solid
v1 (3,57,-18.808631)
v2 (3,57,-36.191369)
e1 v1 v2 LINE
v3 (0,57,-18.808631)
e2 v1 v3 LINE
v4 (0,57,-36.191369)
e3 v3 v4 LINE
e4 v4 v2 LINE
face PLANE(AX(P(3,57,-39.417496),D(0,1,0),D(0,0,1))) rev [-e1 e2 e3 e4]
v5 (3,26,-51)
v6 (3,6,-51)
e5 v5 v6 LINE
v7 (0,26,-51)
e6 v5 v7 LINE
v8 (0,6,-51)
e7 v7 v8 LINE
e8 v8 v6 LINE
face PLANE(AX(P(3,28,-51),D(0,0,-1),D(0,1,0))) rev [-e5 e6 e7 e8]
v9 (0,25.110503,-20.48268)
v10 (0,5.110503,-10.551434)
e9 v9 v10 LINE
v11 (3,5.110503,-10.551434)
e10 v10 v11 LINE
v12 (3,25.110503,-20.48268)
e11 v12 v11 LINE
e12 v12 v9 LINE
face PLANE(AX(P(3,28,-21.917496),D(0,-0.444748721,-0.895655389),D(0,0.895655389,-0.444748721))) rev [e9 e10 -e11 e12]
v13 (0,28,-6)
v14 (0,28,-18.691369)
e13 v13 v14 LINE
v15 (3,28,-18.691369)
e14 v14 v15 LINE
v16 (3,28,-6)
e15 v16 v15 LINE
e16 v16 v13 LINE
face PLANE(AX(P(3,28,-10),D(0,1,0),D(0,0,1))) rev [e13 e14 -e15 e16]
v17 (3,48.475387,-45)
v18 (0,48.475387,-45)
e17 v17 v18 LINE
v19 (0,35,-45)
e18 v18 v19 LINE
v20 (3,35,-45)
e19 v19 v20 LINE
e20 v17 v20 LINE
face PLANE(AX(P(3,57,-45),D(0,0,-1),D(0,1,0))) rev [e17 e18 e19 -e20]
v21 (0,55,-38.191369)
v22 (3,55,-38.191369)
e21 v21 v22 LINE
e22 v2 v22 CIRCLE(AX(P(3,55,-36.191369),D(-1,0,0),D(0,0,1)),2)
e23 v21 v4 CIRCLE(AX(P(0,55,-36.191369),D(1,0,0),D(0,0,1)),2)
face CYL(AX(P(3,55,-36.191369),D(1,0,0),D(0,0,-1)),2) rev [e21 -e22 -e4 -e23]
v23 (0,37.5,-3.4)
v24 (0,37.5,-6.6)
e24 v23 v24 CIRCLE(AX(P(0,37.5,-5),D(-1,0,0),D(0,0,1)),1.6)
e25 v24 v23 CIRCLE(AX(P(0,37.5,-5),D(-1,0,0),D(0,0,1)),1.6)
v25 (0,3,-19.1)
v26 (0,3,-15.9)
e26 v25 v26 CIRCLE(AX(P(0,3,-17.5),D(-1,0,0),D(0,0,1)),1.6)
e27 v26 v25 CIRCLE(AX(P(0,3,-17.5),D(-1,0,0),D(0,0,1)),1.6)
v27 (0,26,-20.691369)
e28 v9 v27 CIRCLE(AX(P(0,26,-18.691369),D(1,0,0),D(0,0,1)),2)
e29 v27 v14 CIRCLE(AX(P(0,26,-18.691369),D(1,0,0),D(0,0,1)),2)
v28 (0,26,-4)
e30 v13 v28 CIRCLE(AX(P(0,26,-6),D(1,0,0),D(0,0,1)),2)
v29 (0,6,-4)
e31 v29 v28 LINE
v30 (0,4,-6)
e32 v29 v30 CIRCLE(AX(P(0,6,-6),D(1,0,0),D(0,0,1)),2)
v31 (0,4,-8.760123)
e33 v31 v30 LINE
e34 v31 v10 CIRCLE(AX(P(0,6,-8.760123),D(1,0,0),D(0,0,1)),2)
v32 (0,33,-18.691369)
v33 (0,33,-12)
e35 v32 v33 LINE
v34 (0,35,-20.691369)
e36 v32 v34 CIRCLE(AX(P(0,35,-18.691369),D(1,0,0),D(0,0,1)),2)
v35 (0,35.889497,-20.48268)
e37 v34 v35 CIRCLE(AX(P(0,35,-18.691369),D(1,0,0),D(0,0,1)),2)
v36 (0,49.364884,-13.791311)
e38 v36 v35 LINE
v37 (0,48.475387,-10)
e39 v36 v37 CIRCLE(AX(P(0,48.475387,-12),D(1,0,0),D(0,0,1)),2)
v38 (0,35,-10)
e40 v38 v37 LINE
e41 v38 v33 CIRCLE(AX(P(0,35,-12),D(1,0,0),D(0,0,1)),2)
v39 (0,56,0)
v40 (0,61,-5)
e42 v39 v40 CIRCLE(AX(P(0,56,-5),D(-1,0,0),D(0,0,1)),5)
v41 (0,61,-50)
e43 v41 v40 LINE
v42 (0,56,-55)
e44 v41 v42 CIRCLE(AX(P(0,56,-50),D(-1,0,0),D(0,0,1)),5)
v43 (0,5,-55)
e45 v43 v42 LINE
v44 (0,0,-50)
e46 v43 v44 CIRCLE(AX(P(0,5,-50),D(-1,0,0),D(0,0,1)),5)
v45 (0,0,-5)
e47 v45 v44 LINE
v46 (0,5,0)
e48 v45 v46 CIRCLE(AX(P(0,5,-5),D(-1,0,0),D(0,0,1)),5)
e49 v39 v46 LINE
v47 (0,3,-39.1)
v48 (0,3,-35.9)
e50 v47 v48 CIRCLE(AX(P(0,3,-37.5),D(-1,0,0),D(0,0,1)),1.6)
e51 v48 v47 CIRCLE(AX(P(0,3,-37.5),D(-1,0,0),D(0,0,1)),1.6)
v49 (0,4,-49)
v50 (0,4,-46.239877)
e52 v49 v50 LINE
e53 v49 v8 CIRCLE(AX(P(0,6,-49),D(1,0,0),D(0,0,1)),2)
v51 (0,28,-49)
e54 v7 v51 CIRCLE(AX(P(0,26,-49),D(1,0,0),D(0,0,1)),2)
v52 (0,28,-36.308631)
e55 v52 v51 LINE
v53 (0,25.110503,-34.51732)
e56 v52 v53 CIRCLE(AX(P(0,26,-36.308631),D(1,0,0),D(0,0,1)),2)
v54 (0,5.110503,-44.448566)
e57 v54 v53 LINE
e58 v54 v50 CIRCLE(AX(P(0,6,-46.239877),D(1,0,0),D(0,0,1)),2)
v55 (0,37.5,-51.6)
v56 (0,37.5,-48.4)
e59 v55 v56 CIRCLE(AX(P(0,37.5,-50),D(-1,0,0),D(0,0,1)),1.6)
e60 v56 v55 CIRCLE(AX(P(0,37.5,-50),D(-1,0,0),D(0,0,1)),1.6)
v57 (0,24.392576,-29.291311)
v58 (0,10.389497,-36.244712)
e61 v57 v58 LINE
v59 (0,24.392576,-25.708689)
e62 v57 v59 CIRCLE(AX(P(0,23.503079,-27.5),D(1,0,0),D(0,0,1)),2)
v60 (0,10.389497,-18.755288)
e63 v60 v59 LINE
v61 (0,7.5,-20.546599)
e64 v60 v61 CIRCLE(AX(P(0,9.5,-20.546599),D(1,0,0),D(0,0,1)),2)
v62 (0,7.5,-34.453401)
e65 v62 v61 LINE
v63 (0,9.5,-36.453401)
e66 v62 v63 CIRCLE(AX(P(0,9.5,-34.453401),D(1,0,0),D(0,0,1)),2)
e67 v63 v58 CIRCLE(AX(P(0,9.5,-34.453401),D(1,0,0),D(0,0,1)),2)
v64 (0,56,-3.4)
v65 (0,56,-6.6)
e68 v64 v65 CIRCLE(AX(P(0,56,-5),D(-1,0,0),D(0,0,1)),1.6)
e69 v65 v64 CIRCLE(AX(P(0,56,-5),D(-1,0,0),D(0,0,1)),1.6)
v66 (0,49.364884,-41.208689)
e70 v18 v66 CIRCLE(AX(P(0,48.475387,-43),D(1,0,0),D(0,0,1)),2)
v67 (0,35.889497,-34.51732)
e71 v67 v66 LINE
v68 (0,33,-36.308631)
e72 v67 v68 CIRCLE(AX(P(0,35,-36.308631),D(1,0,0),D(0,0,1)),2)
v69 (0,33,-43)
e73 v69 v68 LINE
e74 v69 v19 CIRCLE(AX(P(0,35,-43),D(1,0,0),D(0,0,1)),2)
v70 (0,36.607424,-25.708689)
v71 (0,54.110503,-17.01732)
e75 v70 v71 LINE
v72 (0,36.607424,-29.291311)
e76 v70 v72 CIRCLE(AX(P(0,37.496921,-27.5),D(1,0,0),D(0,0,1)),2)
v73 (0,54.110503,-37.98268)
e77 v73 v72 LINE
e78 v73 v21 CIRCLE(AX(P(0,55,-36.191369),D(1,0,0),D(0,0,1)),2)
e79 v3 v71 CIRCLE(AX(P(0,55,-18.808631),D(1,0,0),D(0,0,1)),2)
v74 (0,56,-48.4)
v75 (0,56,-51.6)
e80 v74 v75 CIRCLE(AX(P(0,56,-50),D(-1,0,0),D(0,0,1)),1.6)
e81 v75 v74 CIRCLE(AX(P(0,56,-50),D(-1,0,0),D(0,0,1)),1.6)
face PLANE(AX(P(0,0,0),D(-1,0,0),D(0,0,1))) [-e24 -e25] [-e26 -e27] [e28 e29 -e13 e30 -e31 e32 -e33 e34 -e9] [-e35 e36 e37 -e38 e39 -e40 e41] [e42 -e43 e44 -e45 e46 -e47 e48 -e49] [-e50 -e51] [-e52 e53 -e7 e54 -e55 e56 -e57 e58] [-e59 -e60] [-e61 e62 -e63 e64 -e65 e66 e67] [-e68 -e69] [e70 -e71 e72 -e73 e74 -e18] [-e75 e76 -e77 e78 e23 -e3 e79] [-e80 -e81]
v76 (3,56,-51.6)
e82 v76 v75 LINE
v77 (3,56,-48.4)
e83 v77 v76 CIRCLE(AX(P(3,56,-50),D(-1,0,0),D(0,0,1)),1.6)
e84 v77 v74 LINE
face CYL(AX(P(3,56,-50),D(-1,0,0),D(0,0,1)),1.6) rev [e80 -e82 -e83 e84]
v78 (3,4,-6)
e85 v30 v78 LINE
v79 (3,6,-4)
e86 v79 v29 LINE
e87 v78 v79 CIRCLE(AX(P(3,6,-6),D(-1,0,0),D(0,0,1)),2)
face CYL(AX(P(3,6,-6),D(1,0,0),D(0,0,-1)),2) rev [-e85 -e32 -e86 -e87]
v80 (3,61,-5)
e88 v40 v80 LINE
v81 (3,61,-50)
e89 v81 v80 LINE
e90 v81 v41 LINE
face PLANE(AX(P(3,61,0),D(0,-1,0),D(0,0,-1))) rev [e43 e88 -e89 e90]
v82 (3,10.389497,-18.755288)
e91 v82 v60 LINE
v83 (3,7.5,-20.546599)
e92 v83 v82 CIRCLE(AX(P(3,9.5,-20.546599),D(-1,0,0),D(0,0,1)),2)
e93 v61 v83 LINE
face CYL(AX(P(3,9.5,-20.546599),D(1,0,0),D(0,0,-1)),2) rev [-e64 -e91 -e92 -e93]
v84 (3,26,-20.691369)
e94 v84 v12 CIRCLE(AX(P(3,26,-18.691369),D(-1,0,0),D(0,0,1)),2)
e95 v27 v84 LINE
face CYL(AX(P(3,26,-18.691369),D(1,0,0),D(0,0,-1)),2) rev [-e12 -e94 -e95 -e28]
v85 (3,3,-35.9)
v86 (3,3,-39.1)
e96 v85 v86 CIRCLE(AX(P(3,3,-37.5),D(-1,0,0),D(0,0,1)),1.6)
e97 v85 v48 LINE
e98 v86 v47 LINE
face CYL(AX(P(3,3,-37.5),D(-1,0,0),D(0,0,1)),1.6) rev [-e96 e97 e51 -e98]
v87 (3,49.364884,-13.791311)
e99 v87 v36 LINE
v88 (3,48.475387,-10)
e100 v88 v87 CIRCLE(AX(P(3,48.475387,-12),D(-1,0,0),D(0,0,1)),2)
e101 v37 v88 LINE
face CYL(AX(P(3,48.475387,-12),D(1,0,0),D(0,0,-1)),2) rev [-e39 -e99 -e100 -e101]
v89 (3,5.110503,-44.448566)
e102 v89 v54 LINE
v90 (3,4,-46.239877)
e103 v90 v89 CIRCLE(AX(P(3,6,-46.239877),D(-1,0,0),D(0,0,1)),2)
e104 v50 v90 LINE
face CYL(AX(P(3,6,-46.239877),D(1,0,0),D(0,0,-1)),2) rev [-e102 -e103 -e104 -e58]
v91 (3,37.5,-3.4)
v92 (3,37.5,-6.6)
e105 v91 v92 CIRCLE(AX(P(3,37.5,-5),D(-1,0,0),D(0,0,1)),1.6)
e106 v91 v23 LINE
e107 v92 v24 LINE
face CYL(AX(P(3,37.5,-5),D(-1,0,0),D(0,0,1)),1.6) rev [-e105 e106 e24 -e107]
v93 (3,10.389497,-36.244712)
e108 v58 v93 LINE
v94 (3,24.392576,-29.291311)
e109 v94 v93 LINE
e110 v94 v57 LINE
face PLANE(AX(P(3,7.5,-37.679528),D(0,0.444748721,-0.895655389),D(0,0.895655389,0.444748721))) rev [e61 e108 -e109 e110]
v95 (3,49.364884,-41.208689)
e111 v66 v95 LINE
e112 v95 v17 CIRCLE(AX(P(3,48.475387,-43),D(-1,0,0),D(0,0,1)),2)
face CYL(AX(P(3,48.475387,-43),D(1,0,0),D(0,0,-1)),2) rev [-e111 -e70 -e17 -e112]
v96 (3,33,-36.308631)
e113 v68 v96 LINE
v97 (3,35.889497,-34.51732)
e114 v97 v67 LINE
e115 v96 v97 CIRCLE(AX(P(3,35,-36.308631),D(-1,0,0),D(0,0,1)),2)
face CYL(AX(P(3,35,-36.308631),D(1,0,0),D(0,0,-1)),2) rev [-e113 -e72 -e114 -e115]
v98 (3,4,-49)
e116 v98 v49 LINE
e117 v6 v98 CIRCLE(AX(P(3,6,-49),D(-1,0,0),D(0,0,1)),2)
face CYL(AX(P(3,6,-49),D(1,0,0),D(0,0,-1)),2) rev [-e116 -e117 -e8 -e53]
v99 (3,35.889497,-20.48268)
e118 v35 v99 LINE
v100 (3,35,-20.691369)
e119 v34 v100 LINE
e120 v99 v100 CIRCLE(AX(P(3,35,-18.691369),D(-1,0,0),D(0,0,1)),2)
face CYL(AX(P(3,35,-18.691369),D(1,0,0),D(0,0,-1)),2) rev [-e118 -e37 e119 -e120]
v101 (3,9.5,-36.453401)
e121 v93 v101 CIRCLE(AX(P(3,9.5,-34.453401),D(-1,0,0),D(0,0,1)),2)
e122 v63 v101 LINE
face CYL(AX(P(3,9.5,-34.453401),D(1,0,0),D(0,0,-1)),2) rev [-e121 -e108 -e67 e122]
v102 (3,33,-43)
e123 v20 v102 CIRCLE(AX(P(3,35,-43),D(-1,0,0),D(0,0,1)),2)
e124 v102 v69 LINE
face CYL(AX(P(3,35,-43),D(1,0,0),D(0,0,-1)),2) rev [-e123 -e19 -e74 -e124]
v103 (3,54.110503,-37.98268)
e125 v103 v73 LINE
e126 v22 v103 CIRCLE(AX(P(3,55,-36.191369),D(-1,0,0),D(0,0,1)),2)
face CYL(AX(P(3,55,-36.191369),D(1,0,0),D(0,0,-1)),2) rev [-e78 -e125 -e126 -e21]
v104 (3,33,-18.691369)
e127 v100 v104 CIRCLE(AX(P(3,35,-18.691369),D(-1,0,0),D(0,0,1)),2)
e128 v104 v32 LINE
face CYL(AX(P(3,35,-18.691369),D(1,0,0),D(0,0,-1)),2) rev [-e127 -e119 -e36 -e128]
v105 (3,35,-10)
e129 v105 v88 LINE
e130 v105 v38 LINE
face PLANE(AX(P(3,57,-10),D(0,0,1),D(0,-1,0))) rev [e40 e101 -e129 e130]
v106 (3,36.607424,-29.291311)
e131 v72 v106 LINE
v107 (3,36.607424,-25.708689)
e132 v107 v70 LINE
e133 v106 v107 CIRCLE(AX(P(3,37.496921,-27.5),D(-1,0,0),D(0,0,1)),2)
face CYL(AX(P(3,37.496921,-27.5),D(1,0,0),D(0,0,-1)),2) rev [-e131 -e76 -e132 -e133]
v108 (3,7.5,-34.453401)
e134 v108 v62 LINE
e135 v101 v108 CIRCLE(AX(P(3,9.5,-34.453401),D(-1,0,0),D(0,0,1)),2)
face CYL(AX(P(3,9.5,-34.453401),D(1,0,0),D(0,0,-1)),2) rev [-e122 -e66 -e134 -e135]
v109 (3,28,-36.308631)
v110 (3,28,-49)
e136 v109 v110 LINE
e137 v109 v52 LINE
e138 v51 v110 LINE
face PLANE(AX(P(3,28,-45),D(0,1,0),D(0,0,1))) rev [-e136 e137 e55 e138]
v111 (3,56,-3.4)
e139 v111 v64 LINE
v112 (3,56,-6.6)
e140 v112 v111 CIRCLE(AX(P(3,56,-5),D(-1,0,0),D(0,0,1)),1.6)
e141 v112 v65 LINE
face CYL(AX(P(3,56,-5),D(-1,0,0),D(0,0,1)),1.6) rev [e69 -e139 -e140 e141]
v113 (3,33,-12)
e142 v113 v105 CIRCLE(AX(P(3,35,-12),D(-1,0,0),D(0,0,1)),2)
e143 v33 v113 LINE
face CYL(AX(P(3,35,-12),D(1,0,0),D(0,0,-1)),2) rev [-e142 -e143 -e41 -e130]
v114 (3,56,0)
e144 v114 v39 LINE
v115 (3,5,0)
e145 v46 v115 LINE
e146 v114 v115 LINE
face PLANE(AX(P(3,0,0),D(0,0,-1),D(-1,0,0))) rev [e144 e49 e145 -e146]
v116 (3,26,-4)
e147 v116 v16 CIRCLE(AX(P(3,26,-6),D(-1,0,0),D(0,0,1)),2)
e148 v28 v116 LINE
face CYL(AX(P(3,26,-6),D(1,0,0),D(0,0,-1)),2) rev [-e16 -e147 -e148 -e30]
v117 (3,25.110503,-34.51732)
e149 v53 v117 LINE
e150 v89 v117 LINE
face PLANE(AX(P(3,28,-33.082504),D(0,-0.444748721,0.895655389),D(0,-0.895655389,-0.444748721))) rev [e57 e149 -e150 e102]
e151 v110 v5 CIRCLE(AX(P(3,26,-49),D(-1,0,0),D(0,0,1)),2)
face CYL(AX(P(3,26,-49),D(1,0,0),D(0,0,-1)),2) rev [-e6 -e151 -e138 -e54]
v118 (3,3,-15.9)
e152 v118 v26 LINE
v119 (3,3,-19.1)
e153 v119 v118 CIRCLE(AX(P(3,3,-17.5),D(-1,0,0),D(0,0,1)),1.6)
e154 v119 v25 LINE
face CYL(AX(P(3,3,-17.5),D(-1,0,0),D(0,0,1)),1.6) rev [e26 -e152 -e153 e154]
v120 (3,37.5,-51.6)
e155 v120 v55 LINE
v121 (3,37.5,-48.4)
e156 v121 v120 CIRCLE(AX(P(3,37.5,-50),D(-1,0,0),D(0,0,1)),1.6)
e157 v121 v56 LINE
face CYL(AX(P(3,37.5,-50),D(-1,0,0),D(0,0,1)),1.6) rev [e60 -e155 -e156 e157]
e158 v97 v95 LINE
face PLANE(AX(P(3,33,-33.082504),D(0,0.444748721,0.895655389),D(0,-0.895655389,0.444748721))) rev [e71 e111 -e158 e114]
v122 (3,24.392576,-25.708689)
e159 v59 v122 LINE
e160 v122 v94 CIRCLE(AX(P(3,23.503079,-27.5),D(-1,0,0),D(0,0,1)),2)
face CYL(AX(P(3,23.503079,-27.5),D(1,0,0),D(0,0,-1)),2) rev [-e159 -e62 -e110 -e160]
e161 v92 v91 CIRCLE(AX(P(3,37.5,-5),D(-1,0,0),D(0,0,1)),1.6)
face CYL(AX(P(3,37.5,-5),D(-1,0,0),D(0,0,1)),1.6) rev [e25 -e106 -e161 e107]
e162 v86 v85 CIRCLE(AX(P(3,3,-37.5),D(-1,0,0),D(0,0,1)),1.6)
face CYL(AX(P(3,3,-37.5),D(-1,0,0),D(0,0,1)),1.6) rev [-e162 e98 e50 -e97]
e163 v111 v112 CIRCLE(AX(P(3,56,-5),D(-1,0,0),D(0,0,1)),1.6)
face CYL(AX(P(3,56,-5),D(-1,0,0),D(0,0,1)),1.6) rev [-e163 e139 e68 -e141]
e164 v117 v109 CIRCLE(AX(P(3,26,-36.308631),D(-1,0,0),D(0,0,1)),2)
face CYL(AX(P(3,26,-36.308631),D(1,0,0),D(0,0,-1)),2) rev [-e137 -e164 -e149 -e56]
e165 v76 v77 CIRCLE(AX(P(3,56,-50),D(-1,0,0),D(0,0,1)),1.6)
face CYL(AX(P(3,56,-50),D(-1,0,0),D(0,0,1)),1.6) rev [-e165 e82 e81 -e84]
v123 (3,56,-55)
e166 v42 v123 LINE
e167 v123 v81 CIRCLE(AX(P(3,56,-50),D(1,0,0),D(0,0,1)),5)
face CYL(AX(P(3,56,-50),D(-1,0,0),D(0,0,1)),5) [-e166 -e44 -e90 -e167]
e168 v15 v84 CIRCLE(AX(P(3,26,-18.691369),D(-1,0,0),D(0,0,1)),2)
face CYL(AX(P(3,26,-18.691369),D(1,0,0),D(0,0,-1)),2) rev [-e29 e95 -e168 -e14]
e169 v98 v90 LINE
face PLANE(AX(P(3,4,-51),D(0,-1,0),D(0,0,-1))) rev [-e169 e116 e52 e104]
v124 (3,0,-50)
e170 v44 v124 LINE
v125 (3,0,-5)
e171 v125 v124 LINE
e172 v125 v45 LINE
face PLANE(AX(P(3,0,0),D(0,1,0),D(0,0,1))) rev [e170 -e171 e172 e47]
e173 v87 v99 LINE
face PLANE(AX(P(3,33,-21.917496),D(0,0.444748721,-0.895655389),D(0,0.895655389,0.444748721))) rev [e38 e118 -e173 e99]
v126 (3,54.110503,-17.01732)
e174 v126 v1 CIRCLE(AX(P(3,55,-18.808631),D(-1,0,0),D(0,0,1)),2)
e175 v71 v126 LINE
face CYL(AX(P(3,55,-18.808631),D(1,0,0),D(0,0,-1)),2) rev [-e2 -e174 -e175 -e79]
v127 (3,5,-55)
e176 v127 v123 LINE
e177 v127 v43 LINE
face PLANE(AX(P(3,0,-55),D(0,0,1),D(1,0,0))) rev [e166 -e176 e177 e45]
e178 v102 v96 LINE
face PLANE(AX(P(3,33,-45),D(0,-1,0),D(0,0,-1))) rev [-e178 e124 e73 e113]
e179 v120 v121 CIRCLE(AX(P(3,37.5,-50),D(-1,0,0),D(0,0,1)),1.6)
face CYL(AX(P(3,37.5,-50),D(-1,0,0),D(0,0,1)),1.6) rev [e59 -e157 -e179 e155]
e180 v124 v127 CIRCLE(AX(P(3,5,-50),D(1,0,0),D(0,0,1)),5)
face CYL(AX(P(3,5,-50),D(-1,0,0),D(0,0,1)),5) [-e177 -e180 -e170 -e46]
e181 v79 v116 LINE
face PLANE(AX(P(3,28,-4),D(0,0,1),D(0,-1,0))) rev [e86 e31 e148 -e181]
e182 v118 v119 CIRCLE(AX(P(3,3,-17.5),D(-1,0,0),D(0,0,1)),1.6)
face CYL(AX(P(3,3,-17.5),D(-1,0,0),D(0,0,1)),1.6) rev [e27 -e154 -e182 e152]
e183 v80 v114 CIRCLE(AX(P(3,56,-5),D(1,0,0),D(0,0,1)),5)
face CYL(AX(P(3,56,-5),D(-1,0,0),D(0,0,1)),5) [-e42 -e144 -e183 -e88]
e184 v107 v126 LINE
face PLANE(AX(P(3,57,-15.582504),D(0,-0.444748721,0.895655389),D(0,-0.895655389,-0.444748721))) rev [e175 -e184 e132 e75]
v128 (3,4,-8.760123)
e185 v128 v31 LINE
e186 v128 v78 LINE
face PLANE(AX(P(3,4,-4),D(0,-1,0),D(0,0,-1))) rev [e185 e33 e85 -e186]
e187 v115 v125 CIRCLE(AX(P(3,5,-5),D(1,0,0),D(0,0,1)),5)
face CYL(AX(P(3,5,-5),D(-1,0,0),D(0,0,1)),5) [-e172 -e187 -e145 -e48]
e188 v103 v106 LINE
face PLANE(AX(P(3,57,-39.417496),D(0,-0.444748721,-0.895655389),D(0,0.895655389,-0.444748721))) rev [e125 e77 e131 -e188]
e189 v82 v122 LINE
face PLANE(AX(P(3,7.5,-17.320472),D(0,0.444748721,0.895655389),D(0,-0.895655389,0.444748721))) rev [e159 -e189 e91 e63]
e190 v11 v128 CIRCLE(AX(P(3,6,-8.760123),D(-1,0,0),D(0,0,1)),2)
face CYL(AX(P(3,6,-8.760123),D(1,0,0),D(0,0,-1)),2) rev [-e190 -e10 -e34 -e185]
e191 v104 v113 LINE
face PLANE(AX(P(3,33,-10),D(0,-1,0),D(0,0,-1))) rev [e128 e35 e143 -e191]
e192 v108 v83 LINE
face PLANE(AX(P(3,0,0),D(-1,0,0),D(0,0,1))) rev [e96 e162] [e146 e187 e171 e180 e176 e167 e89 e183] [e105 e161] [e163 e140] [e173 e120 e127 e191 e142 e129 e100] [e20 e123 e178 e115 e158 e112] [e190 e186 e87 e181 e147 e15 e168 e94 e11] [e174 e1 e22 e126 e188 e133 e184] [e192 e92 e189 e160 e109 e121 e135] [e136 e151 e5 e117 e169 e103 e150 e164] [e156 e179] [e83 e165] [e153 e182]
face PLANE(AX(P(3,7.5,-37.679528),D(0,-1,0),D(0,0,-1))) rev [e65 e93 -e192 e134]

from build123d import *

# Parameters (mm, degrees)
SKETCH_2_W          = 55
SKETCH_2_H          = 61
EXTRUDE_1_DEPTH     = 3
SKETCH_3_R          = 1.6
CUT_EXTRUDE_1_DEPTH = 3
FILLET_1_R          = 5
CUT_EXTRUDE_2_DEPTH = 3
FILLET_2_R          = 2


with BuildPart() as part:
    # 草图2 → 凸台-拉伸1 (new body)
    with BuildSketch(Plane(origin=(0, 0, 0), x_dir=(0, 0, -1), z_dir=(1, 0, 0))):
        with Locations((27.5, 30.5)):
            Rectangle(SKETCH_2_W, SKETCH_2_H)
    extrude(amount=EXTRUDE_1_DEPTH)

    # 草图3 → 切除-拉伸1 (cut)
    with BuildSketch(Plane.ZY):
        with Locations((-5, 56)):
            Circle(SKETCH_3_R)
        with Locations((-5, 37.5)):
            Circle(SKETCH_3_R)
        with Locations((-50, 56)):
            Circle(SKETCH_3_R)
        with Locations((-50, 37.5)):
            Circle(SKETCH_3_R)
        with Locations((-37.5, 3)):
            Circle(SKETCH_3_R)
        with Locations((-17.5, 3)):
            Circle(SKETCH_3_R)
    extrude(amount=-CUT_EXTRUDE_1_DEPTH, mode=Mode.SUBTRACT)

    # 圆角1
    fillet_1_edges = [part.edges().sort_by_distance(p)[0] for p in [
        (1.5, 61, 0),
        (1.5, 61, -55),
        (1.5, 0, -55),
        (1.5, 0, 0),
    ]]
    fillet(fillet_1_edges, radius=FILLET_1_R)

    # 草图4 → 切除-拉伸2 (cut)
    with BuildSketch(Plane.ZY):
        Polygon((-39.417495765, 57), (-27.5, 33), (-15.582504235, 57), align=None)
        Polygon((-45, 57), (-45, 33), (-33.082504235, 33), align=None)
        Polygon((-21.917495765, 33), (-10, 57), (-10, 33), align=None)
        Polygon((-10, 28), (-21.917495765, 28), (-10, 4), (-4, 4), (-4, 28), align=None)
        Polygon((-37.679527633, 7.5), (-27.5, 28), (-17.320472367, 7.5), align=None)
        Polygon((-45, 28), (-33.082504235, 28), (-45, 4), (-51, 4), (-51, 28), align=None)
    extrude(amount=-CUT_EXTRUDE_2_DEPTH, mode=Mode.SUBTRACT)

    # 圆角2
    fillet_2_edges = [part.edges().sort_by_distance(p)[0] for p in [
        (1.5, 57, -45),
        (1.5, 33, -33.082504235),
        (1.5, 33, -45),
        (1.5, 57, -39.417495765),
        (1.5, 57, -15.582504235),
        (1.5, 33, -27.5),
        (1.5, 28, -27.5),
        (1.5, 7.5, -17.320472367),
        (1.5, 7.5, -37.679527633),
        (1.5, 28, -4),
        (1.5, 4, -4),
        (1.5, 4, -10),
        (1.5, 28, -21.917495765),
        (1.5, 4, -51),
        (1.5, 28, -51),
        (1.5, 28, -33.082504235),
        (1.5, 4, -45),
        (1.5, 33, -10),
        (1.5, 33, -21.917495765),
        (1.5, 57, -10),
    ]]
    fillet(fillet_2_edges, radius=FILLET_2_R)


solid = part.part
